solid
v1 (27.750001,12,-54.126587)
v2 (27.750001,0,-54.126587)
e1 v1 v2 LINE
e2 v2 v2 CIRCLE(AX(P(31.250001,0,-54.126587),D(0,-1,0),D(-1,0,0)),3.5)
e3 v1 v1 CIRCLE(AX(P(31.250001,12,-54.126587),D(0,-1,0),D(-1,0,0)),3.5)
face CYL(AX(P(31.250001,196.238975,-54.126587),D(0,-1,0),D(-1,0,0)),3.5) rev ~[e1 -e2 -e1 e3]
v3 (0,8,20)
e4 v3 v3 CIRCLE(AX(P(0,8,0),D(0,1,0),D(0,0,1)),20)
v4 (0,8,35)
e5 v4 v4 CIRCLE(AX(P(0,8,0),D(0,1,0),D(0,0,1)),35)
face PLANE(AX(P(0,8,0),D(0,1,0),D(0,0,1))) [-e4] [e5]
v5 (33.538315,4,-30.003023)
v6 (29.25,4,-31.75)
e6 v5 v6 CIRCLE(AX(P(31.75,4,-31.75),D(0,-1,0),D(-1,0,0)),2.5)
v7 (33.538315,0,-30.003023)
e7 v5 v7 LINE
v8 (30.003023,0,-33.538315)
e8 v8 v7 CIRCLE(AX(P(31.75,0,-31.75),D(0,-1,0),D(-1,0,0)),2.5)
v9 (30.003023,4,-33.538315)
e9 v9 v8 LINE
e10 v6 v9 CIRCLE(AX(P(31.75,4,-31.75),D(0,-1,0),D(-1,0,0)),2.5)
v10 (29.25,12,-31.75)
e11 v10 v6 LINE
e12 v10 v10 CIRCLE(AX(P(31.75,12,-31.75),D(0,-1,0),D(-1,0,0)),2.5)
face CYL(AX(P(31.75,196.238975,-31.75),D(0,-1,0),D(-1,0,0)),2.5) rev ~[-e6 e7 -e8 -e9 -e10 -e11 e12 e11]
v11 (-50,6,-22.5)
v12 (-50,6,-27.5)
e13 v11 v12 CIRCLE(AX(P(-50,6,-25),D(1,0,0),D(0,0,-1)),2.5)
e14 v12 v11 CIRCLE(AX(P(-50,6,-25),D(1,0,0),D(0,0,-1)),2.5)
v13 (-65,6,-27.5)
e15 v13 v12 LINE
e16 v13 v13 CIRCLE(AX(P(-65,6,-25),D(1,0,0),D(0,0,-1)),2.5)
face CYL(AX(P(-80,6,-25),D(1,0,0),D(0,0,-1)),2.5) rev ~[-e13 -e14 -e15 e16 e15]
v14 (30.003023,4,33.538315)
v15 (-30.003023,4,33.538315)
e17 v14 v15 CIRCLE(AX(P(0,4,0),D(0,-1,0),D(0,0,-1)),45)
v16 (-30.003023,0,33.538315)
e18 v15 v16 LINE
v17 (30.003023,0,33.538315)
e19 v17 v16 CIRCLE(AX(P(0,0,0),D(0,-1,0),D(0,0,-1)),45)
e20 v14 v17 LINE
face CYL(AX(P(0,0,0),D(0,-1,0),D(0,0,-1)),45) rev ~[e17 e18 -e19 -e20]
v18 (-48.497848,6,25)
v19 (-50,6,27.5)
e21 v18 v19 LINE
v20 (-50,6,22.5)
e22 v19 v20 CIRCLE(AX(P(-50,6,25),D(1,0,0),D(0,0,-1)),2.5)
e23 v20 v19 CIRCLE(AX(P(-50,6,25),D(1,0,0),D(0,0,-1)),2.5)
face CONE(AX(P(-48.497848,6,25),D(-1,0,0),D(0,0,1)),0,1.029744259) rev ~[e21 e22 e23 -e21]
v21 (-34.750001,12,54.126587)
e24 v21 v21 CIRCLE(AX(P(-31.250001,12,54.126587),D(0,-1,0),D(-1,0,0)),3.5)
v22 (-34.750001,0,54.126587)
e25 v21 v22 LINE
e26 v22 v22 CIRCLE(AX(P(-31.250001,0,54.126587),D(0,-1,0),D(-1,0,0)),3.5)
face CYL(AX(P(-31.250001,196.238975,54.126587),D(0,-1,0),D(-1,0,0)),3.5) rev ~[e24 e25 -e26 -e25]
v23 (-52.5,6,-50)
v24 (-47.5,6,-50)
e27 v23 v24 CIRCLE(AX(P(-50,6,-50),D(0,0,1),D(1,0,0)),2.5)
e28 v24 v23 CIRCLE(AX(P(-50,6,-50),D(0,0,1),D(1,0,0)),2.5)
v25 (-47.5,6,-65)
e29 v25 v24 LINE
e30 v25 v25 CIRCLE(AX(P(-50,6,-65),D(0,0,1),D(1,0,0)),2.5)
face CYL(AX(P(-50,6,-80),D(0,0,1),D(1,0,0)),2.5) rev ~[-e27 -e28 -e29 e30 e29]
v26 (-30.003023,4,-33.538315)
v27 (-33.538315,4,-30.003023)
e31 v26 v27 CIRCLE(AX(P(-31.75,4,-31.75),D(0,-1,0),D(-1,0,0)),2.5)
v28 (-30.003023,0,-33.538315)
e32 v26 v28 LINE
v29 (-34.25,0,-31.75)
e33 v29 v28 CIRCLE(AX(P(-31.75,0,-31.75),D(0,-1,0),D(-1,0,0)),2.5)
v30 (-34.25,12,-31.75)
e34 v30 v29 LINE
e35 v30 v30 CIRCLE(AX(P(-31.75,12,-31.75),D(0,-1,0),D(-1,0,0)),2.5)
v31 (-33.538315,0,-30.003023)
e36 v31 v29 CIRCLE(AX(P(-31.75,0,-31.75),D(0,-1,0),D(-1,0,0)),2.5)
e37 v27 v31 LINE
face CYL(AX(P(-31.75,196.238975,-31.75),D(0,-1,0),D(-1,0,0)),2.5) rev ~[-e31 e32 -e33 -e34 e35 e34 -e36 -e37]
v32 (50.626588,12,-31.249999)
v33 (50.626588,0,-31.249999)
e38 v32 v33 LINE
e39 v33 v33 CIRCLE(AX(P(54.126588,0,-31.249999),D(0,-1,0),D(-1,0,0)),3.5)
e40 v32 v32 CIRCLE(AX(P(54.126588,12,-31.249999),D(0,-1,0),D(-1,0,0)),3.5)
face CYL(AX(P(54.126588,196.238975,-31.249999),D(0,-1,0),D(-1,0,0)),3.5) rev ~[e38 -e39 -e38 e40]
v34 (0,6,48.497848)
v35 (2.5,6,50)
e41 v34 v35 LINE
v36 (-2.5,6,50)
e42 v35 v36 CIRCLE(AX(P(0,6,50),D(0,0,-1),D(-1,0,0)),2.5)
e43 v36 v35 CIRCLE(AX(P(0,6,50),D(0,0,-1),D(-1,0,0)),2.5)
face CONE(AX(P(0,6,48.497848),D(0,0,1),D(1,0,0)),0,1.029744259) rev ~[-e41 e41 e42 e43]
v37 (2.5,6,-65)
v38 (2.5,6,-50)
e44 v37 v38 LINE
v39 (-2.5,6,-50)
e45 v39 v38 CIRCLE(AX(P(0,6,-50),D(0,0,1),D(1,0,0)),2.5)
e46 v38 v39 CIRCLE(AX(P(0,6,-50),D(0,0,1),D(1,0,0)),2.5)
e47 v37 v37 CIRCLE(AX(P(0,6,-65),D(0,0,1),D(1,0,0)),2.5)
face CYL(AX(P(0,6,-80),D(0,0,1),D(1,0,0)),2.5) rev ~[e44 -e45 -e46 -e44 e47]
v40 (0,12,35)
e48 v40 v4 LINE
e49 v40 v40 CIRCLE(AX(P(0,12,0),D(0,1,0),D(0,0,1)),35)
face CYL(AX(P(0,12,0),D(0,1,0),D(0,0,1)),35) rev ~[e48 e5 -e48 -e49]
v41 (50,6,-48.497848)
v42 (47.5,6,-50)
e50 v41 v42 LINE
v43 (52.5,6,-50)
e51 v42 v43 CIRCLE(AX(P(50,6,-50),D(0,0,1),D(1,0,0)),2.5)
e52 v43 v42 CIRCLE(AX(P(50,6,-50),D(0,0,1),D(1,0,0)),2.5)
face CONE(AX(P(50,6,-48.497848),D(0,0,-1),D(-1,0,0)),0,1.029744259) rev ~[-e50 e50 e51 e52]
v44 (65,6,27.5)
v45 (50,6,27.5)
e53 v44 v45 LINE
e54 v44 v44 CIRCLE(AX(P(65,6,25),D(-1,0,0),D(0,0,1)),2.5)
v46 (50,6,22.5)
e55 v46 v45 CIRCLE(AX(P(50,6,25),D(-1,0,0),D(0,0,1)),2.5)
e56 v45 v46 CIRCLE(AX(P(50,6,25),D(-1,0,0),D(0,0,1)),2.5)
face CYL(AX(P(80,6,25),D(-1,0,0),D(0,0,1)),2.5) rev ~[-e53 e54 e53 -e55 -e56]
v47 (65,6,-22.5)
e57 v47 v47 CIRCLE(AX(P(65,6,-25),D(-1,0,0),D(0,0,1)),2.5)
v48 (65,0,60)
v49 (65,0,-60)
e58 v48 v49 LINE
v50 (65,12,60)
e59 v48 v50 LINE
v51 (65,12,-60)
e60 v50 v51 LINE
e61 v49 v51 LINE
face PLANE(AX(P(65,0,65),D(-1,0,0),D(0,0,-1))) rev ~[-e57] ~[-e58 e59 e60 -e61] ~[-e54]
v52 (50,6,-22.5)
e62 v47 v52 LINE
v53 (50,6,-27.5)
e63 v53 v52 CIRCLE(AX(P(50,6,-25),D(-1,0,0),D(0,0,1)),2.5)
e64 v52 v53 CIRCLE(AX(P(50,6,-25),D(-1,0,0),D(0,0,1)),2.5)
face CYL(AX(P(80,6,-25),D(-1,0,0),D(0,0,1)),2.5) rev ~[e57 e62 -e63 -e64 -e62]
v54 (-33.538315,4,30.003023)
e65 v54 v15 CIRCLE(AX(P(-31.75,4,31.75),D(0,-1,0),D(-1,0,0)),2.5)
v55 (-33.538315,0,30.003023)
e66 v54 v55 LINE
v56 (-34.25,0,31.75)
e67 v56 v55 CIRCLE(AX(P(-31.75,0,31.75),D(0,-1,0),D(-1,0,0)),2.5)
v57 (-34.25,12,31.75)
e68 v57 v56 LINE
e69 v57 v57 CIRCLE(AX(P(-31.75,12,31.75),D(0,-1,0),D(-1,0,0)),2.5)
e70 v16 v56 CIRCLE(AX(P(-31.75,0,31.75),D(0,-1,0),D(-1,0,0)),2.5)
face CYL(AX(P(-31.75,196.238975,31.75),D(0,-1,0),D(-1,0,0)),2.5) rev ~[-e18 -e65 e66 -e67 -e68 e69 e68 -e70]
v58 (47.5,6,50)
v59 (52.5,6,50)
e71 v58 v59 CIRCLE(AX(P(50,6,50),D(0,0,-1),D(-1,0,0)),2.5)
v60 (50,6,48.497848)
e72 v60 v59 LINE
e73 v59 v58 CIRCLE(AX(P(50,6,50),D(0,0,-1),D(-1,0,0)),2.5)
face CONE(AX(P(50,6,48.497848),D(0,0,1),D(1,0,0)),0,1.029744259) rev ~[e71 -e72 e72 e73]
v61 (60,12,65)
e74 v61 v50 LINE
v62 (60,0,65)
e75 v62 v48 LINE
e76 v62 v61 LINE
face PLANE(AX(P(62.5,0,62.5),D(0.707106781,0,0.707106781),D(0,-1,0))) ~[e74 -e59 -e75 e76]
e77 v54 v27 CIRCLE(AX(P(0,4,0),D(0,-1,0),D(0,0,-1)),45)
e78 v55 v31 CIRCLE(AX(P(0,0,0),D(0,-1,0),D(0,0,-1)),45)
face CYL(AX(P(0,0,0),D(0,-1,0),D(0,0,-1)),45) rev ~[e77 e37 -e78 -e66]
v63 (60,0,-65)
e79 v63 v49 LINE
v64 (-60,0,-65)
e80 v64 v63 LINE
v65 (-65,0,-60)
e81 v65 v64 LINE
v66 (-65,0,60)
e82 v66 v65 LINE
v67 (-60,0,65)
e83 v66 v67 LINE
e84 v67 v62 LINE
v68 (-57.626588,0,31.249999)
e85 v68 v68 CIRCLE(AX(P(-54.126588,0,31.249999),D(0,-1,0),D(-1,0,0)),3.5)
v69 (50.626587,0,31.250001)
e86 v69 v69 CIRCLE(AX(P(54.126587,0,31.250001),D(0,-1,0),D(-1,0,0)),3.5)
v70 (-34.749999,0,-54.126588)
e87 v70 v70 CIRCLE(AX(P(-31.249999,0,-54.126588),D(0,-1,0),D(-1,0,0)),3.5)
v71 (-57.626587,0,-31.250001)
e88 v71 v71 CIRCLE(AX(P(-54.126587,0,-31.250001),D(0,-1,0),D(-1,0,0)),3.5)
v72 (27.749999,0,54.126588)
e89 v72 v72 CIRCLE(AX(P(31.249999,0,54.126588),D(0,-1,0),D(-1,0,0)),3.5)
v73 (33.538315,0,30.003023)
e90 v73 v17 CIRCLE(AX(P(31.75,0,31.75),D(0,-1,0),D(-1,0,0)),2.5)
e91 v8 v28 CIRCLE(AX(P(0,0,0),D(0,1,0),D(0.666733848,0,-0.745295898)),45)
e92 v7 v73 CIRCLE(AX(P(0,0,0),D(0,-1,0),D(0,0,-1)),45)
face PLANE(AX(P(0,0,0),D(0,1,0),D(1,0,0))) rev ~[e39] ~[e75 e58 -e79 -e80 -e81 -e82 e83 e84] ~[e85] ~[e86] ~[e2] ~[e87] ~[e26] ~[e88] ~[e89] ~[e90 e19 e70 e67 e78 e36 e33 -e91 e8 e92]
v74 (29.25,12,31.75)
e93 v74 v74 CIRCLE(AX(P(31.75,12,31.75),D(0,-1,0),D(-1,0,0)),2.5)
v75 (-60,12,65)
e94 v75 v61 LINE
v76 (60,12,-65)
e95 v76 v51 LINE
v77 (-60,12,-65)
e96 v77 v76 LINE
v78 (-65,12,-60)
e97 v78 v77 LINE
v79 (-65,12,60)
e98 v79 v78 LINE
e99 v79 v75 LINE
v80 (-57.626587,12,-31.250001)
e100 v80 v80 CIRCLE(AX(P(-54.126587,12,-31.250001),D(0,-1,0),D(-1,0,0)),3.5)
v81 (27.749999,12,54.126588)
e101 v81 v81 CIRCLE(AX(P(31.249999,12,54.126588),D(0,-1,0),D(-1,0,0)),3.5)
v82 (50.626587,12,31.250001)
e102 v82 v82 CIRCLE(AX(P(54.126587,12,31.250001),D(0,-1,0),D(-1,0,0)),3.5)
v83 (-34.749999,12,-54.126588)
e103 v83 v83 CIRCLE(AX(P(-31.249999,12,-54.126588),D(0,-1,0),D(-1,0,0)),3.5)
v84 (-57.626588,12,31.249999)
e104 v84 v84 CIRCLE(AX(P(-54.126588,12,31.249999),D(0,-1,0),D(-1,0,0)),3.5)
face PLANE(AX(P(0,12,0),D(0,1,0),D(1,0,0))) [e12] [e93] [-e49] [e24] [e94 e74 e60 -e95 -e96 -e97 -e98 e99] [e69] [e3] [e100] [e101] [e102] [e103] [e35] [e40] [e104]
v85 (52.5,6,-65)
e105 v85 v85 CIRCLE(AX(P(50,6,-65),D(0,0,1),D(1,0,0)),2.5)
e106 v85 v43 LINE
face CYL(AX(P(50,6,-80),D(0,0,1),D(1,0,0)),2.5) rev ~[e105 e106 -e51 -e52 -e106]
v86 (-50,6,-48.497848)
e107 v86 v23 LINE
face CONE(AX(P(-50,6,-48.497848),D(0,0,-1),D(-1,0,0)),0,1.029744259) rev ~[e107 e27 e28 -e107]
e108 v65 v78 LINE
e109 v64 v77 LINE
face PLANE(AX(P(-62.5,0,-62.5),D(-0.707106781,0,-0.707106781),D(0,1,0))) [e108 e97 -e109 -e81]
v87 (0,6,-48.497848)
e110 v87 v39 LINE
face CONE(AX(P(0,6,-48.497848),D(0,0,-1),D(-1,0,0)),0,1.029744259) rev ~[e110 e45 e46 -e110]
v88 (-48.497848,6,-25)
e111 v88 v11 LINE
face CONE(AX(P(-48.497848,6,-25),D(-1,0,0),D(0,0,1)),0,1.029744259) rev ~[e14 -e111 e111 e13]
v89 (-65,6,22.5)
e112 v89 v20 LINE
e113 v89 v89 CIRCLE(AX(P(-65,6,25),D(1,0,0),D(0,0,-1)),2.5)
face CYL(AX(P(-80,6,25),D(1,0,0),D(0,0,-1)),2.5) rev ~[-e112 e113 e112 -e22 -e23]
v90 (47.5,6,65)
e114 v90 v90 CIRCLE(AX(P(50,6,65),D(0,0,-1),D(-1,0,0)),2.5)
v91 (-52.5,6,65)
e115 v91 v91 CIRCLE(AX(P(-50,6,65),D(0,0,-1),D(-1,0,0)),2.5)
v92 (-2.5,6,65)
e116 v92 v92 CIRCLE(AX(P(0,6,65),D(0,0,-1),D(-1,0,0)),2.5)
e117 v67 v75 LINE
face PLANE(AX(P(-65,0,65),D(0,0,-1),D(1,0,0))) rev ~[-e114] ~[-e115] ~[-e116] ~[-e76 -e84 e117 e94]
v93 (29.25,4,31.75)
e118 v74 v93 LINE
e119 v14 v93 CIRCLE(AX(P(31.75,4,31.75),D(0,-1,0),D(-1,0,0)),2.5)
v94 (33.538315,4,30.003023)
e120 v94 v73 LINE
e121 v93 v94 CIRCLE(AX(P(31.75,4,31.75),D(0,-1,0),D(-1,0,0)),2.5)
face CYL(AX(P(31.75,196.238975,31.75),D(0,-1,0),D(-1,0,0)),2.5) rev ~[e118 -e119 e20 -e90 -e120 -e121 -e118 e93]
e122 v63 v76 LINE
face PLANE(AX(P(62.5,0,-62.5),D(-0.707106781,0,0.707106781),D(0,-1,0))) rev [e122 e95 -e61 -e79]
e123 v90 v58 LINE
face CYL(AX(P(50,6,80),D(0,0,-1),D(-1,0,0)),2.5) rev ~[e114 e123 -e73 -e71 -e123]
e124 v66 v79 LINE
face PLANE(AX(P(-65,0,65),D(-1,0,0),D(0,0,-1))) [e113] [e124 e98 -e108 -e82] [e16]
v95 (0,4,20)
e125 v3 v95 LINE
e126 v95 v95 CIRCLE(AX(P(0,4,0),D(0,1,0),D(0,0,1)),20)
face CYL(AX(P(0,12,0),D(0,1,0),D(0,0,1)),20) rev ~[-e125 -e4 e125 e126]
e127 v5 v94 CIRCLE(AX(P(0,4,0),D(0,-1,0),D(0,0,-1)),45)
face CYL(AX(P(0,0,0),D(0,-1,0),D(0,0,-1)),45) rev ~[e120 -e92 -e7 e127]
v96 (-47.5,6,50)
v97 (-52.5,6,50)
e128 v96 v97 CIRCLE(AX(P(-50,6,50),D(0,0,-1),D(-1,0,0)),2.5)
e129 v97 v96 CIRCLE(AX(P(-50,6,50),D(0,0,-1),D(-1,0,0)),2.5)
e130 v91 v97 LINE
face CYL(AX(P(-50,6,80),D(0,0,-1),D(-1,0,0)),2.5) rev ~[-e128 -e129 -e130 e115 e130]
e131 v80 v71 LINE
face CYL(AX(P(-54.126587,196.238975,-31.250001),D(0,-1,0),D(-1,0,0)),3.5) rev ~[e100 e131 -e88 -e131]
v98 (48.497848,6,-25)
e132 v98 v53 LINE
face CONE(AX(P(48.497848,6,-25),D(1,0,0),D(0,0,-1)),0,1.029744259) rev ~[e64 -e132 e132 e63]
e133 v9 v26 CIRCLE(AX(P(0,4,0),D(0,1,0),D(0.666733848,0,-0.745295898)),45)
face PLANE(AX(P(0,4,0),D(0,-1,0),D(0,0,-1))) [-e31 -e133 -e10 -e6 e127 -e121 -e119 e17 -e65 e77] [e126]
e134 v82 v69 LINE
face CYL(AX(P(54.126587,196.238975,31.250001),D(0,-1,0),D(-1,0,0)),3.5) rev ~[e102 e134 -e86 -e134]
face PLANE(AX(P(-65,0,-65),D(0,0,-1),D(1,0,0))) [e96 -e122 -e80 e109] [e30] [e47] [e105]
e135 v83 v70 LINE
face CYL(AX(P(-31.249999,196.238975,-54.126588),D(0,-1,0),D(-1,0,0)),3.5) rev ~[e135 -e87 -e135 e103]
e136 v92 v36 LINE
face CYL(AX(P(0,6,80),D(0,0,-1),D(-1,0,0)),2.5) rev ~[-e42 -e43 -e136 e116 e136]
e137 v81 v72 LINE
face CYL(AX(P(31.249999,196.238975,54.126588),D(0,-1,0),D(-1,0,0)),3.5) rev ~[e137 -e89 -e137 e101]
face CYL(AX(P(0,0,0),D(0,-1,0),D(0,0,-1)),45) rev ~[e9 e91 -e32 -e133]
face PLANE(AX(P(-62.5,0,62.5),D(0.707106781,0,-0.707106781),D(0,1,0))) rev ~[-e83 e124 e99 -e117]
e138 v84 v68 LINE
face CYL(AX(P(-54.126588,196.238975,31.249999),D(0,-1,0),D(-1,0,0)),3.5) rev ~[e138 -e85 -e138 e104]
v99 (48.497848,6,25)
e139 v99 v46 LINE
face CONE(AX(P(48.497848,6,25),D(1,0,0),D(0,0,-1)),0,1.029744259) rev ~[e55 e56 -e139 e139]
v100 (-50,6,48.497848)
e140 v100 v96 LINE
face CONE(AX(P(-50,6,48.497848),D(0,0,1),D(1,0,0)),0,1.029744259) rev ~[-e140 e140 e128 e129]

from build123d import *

# Parameters (mm, degrees)
SKETCH_1_W             = 130
SKETCH_1_H             = 130
EXTRUDE_1_DEPTH        = 12
SKETCH_2_R             = 20
CUT_EXTRUDE_1_DEPTH    = 93.703829479
HOLE_WIZARD_M6_1_D     = 7
SKETCH_5_R             = 35
CUT_EXTRUDE_2_DEPTH    = 4
SKETCH_6_R             = 45
CUT_EXTRUDE_3_DEPTH    = 4
HOLE_WIZARD_M6_1_2_D   = 5
HOLE_WIZARD_M6_2_D     = 5
HOLE_WIZARD_M6_2_DEPTH = 15
HOLE_WIZARD_M6_2_TIP   = 1.502151548
HOLE_WIZARD_M6_3_D     = 5
HOLE_WIZARD_M6_3_DEPTH = 15
HOLE_WIZARD_M6_3_TIP   = 1.502151548
HOLE_WIZARD_M6_4_D     = 5
HOLE_WIZARD_M6_4_DEPTH = 15
HOLE_WIZARD_M6_4_TIP   = 1.502151548
HOLE_WIZARD_M6_5_D     = 5
HOLE_WIZARD_M6_5_DEPTH = 15
HOLE_WIZARD_M6_5_TIP   = 1.502151548
CHAMFER_1_SIZE         = 5


with BuildPart() as part:
    # 草图1 → 凸台-拉伸1 (new body)
    with BuildSketch(Plane(origin=(0, 0, 0), x_dir=(1, 0, 0), z_dir=(0, 1, 0))):
        Rectangle(SKETCH_1_W, SKETCH_1_H)
    extrude(amount=EXTRUDE_1_DEPTH)

    # 草图2 → 切除-拉伸1 (cut, through all)
    with BuildSketch(Plane(origin=(0, 12, 0), x_dir=(1, 0, 0), z_dir=(0, 1, 0))):
        with Locations(Location((0, 0, 0), (0, 0, 270))):
            Circle(SKETCH_2_R)
    extrude(amount=-CUT_EXTRUDE_1_DEPTH, mode=Mode.SUBTRACT)

    # Hole Wizard M6 _1 (through all)
    with Locations(Plane(origin=(0, 12, 0), x_dir=(1, 0, 0), z_dir=(0, 1, 0))):
        with Locations((31.250000582, 54.1265874), (54.126588073, 31.249999418), (54.1265874, -31.250000582), (31.249999418, -54.126588073), (-31.250000582, -54.1265874), (-54.126588073, -31.249999418), (-54.1265874, 31.250000582), (-31.249999418, 54.126588073)):
            Hole(HOLE_WIZARD_M6_1_D / 2)

    # 草图5 → 切除-拉伸2 (cut)
    with BuildSketch(Plane(origin=(0, 12, 0), x_dir=(1, 0, 0), z_dir=(0, 1, 0))):
        with Locations(Location((0, 0, 0), (0, 0, 270))):
            Circle(SKETCH_5_R)
    extrude(amount=-CUT_EXTRUDE_2_DEPTH, mode=Mode.SUBTRACT)

    # 草图6 → 切除-拉伸3 (cut)
    with BuildSketch(Plane.XZ):
        with Locations(Location((0, 0, 0), (0, 0, 270))):
            Circle(SKETCH_6_R)
    extrude(amount=-CUT_EXTRUDE_3_DEPTH, mode=Mode.SUBTRACT)

    # Hole Wizard M6 _1 2 (through all)
    with Locations(Plane(origin=(0, 12, 0), x_dir=(1, 0, 0), z_dir=(0, 1, 0))):
        with Locations((-31.75, 31.75), (31.75, 31.75), (31.75, -31.75), (-31.75, -31.75)):
            Hole(HOLE_WIZARD_M6_1_2_D / 2)

    # M6 螺纹孔2
    with Locations(Plane.ZY.offset(65)):
        with Locations((-25, 6), (25, 6)):
            Hole(HOLE_WIZARD_M6_2_D / 2, depth=HOLE_WIZARD_M6_2_DEPTH)
            with Locations((0, 0, -(HOLE_WIZARD_M6_2_DEPTH + HOLE_WIZARD_M6_2_TIP / 2))):  # 118° drill point
                Cone(0, HOLE_WIZARD_M6_2_D / 2, HOLE_WIZARD_M6_2_TIP, mode=Mode.SUBTRACT)

    # M6 螺纹孔3
    with Locations(Plane(origin=(65, 0, 0), x_dir=(0, 0, -1), z_dir=(1, 0, 0))):
        with Locations((-25, 6), (25, 6)):
            Hole(HOLE_WIZARD_M6_3_D / 2, depth=HOLE_WIZARD_M6_3_DEPTH)
            with Locations((0, 0, -(HOLE_WIZARD_M6_3_DEPTH + HOLE_WIZARD_M6_3_TIP / 2))):  # 118° drill point
                Cone(0, HOLE_WIZARD_M6_3_D / 2, HOLE_WIZARD_M6_3_TIP, mode=Mode.SUBTRACT)

    # M6 螺纹孔4
    with Locations(Plane.XY.offset(65)):
        with Locations((-50, 6), (50, 6), (0, 6)):
            Hole(HOLE_WIZARD_M6_4_D / 2, depth=HOLE_WIZARD_M6_4_DEPTH)
            with Locations((0, 0, -(HOLE_WIZARD_M6_4_DEPTH + HOLE_WIZARD_M6_4_TIP / 2))):  # 118° drill point
                Cone(0, HOLE_WIZARD_M6_4_D / 2, HOLE_WIZARD_M6_4_TIP, mode=Mode.SUBTRACT)

    # M6 螺纹孔5
    with Locations(Plane(origin=(0, 0, -65), x_dir=(-1, 0, 0), z_dir=(0, 0, -1))):
        with Locations((-50, 6), (50, 6), (0, 6)):
            Hole(HOLE_WIZARD_M6_5_D / 2, depth=HOLE_WIZARD_M6_5_DEPTH)
            with Locations((0, 0, -(HOLE_WIZARD_M6_5_DEPTH + HOLE_WIZARD_M6_5_TIP / 2))):  # 118° drill point
                Cone(0, HOLE_WIZARD_M6_5_D / 2, HOLE_WIZARD_M6_5_TIP, mode=Mode.SUBTRACT)

    # 倒角1
    chamfer_1_edges = [part.edges().sort_by_distance(p)[0] for p in [
        (65, 6, 65),
        (-65, 6, 65),
        (-65, 6, -65),
        (65, 6, -65),
    ]]
    chamfer(chamfer_1_edges, length=CHAMFER_1_SIZE)


solid = part.part
